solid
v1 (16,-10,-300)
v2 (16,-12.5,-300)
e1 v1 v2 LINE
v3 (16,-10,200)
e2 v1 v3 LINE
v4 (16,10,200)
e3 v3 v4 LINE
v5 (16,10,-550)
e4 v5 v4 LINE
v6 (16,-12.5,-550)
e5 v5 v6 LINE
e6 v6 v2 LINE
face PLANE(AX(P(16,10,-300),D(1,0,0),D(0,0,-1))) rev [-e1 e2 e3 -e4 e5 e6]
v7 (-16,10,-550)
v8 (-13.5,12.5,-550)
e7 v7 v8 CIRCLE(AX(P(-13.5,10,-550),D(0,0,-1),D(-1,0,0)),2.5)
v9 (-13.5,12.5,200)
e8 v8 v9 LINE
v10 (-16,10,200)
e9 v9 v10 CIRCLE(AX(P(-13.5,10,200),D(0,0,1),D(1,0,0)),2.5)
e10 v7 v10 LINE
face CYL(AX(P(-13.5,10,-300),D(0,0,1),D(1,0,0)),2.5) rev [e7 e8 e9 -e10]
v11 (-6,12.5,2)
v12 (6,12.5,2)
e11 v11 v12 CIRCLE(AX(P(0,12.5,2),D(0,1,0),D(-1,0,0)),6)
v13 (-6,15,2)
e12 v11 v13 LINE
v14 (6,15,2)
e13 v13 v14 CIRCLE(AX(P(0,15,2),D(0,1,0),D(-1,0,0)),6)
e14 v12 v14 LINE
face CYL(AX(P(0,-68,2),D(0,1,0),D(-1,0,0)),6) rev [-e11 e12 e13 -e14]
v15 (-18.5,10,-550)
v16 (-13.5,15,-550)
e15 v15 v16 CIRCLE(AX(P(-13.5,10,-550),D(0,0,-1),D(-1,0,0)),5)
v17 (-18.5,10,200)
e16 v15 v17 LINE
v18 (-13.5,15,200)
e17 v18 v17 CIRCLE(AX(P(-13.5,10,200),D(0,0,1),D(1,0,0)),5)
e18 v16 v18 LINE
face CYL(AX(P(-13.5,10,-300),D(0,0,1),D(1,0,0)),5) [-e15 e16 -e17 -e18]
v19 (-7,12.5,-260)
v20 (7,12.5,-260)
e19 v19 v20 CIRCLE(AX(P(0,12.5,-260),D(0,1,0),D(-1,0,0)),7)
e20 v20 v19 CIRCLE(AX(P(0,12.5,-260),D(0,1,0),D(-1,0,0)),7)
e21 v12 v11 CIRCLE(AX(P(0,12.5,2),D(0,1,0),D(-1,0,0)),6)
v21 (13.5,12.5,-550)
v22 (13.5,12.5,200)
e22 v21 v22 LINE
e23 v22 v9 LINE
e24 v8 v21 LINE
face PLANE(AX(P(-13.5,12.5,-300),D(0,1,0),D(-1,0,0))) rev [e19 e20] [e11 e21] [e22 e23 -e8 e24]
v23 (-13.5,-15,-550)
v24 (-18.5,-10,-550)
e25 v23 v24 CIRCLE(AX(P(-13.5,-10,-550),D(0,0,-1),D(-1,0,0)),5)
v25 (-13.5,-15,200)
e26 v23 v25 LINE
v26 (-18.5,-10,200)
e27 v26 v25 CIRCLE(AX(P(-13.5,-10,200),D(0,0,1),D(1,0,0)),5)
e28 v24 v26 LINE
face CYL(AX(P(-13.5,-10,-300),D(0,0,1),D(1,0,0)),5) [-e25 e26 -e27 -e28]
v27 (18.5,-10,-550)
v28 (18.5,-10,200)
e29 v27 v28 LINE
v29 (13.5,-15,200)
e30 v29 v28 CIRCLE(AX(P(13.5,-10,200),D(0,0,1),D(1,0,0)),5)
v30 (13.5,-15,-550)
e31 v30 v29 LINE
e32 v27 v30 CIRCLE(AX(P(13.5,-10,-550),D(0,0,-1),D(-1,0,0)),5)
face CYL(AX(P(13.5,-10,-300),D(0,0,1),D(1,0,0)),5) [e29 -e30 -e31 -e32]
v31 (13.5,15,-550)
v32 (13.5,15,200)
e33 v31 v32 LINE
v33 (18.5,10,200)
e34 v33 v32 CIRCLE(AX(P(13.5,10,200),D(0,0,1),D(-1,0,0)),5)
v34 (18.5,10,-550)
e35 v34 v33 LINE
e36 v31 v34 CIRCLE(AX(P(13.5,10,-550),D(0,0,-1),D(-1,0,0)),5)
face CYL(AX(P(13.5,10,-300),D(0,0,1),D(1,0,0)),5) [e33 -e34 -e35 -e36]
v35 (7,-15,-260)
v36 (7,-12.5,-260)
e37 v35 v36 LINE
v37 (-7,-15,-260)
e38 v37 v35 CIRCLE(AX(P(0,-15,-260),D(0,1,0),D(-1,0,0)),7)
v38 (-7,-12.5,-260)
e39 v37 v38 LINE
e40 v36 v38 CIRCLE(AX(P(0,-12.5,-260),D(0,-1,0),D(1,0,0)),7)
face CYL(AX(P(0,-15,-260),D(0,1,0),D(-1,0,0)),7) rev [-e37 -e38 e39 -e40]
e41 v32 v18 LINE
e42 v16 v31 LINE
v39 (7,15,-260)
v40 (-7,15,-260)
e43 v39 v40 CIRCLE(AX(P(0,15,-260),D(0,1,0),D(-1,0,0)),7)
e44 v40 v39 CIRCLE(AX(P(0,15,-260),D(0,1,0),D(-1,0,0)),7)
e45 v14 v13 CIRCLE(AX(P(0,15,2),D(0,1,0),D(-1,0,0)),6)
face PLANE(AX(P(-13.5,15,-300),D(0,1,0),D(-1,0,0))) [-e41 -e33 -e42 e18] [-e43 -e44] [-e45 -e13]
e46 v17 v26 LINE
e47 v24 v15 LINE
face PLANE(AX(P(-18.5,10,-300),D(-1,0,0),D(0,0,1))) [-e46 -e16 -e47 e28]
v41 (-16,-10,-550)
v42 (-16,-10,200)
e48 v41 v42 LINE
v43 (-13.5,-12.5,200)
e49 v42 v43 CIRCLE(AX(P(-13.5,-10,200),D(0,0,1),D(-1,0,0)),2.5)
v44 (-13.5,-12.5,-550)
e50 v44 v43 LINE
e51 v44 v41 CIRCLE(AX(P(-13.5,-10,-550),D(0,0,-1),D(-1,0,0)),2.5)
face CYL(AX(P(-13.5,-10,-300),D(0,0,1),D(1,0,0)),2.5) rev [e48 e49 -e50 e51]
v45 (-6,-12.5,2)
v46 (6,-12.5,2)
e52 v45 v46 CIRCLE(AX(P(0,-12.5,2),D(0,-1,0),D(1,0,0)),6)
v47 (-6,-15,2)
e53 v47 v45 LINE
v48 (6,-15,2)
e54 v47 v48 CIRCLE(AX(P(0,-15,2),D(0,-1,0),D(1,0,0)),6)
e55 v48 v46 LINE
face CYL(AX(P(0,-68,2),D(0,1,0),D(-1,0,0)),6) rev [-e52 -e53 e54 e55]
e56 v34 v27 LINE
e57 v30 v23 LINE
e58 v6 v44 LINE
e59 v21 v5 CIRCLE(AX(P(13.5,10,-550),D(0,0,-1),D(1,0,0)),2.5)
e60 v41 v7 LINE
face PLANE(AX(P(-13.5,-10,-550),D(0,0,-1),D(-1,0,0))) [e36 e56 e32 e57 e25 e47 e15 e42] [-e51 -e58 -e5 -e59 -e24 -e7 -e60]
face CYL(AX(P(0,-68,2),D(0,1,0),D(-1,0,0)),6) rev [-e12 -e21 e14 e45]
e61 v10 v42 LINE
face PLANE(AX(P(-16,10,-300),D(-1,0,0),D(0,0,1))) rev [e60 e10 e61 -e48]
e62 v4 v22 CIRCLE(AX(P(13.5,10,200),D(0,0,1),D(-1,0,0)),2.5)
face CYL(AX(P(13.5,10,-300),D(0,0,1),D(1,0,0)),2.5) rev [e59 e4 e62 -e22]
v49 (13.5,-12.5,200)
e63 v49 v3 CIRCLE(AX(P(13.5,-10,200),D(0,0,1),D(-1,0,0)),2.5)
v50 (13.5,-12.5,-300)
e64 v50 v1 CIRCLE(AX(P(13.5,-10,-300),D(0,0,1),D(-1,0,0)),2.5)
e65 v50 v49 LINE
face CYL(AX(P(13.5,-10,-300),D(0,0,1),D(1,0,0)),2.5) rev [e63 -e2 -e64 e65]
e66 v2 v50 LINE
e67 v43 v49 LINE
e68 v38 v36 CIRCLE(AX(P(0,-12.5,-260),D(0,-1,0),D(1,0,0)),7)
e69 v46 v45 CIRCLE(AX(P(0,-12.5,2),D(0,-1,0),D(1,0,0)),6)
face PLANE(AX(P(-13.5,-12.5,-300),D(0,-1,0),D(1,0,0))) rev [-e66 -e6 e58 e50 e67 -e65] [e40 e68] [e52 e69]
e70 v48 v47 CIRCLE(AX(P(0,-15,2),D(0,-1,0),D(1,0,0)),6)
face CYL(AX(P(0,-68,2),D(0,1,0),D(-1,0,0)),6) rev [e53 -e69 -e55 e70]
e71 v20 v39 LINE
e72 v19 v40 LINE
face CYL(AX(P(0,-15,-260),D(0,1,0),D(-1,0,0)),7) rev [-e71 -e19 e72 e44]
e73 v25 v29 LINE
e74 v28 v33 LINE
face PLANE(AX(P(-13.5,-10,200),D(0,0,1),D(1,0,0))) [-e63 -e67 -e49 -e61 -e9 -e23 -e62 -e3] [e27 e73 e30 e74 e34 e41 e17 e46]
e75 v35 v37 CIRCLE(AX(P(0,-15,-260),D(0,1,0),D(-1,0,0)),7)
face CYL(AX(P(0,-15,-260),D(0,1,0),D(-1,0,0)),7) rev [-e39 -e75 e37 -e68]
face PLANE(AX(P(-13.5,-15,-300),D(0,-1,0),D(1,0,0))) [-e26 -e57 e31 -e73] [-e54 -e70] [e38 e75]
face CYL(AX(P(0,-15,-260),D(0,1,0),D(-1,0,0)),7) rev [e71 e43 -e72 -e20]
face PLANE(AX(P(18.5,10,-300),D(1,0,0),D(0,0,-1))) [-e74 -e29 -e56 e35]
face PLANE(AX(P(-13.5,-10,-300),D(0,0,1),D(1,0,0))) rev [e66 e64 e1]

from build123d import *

# Parameters (mm, degrees)
EXTRUDE_1_DEPTH          = 200
EXTRUDE_1_DEPTH_BACK     = 300
SKETCH_7_R               = 6
CUT_EXTRUDE_2_DEPTH      = 83
CUT_EXTRUDE_3_DEPTH      = 303.063321176
CUT_EXTRUDE_3_DEPTH_BACK = 303.063321176
SKETCH_8_R               = 7
EXTRUDE_START            = 250
EXTRUDE_4_DEPTH          = 250


with BuildPart() as part:
    # Sketch 205 → 凸台-拉伸1 (new, two sides: drawn at the far end of the back side and taken through both)
    with BuildSketch(Plane.XY.offset(-EXTRUDE_1_DEPTH_BACK)):
        with BuildLine():
            Line((-13.5, 15), (13.5, 15))
            ThreePointArc((13.5, 15), (17.035533906, 13.535533906), (18.5, 10))
            Line((18.5, 10), (18.5, -10))
            ThreePointArc((18.5, -10), (17.035533906, -13.535533906), (13.5, -15))
            Line((13.5, -15), (-13.5, -15))
            ThreePointArc((-13.5, -15), (-17.035533906, -13.535533906), (-18.5, -10))
            Line((-18.5, -10), (-18.5, 10))
            ThreePointArc((-18.5, 10), (-17.035533906, 13.535533906), (-13.5, 15))
        make_face()
        with BuildLine():
            Line((-13.5, 12.5), (13.5, 12.5))
            ThreePointArc((13.5, 12.5), (15.267766953, 11.767766953), (16, 10))
            Line((16, 10), (16, -10))
            ThreePointArc((16, -10), (15.267766953, -11.767766953), (13.5, -12.5))
            Line((13.5, -12.5), (-13.5, -12.5))
            ThreePointArc((-13.5, -12.5), (-15.267766953, -11.767766953), (-16, -10))
            Line((-16, -10), (-16, 10))
            ThreePointArc((-16, 10), (-15.267766953, 11.767766953), (-13.5, 12.5))
        make_face(mode=Mode.SUBTRACT)
    extrude(amount=EXTRUDE_1_DEPTH + EXTRUDE_1_DEPTH_BACK)

    # 草图7 → 切除-拉伸2 (cut)
    with BuildSketch(Plane(origin=(0, 15, 0), x_dir=(1, 0, 0), z_dir=(0, 1, 0))):
        with Locations((0, -2)):
            Circle(SKETCH_7_R)
    extrude(amount=-CUT_EXTRUDE_2_DEPTH, mode=Mode.SUBTRACT)

    # 草图8 → 切除-拉伸3 (cut, two sides: drawn at the far end of the back side and taken through both)
    with BuildSketch(Plane(origin=(0, 15, 0), x_dir=(1, 0, 0), z_dir=(0, 1, 0)).offset(-CUT_EXTRUDE_3_DEPTH_BACK)):
        with Locations(Location((0, 260, 0), (0, 0, 180))):
            Circle(SKETCH_8_R)
    extrude(amount=CUT_EXTRUDE_3_DEPTH + CUT_EXTRUDE_3_DEPTH_BACK, mode=Mode.SUBTRACT)

    # 草图11 → 凸台-拉伸4 (add)
    with BuildSketch(Plane(origin=(0, 0, -300), x_dir=(-1, 0, 0), z_dir=(0, 0, -1)).offset(EXTRUDE_START)):
        with BuildLine():
            Line((18.5, -10), (18.5, 10))
            ThreePointArc((18.5, 10), (17.035533906, 13.535533906), (13.5, 15))
            Line((13.5, 15), (-13.5, 15))
            ThreePointArc((-13.5, 15), (-17.035533906, 13.535533906), (-18.5, 10))
            Line((-18.5, 10), (-18.5, -10))
            ThreePointArc((-18.5, -10), (-17.035533906, -13.535533906), (-13.5, -15))
            Line((-13.5, -15), (13.5, -15))
            ThreePointArc((13.5, -15), (17.035533906, -13.535533906), (18.5, -10))
        make_face()
        with BuildLine():
            Line((-16, -12.5), (13.5, -12.5))
            ThreePointArc((13.5, -12.5), (15.267766953, -11.767766953), (16, -10))
            Line((16, -10), (16, 10))
            ThreePointArc((16, 10), (15.267766953, 11.767766953), (13.5, 12.5))
            Line((13.5, 12.5), (-13.5, 12.5))
            ThreePointArc((-13.5, 12.5), (-15.267766953, 11.767766953), (-16, 10))
            Line((-16, 10), (-16, -12.5))
        make_face(mode=Mode.SUBTRACT)
    extrude(amount=-EXTRUDE_4_DEPTH)


solid = part.part
